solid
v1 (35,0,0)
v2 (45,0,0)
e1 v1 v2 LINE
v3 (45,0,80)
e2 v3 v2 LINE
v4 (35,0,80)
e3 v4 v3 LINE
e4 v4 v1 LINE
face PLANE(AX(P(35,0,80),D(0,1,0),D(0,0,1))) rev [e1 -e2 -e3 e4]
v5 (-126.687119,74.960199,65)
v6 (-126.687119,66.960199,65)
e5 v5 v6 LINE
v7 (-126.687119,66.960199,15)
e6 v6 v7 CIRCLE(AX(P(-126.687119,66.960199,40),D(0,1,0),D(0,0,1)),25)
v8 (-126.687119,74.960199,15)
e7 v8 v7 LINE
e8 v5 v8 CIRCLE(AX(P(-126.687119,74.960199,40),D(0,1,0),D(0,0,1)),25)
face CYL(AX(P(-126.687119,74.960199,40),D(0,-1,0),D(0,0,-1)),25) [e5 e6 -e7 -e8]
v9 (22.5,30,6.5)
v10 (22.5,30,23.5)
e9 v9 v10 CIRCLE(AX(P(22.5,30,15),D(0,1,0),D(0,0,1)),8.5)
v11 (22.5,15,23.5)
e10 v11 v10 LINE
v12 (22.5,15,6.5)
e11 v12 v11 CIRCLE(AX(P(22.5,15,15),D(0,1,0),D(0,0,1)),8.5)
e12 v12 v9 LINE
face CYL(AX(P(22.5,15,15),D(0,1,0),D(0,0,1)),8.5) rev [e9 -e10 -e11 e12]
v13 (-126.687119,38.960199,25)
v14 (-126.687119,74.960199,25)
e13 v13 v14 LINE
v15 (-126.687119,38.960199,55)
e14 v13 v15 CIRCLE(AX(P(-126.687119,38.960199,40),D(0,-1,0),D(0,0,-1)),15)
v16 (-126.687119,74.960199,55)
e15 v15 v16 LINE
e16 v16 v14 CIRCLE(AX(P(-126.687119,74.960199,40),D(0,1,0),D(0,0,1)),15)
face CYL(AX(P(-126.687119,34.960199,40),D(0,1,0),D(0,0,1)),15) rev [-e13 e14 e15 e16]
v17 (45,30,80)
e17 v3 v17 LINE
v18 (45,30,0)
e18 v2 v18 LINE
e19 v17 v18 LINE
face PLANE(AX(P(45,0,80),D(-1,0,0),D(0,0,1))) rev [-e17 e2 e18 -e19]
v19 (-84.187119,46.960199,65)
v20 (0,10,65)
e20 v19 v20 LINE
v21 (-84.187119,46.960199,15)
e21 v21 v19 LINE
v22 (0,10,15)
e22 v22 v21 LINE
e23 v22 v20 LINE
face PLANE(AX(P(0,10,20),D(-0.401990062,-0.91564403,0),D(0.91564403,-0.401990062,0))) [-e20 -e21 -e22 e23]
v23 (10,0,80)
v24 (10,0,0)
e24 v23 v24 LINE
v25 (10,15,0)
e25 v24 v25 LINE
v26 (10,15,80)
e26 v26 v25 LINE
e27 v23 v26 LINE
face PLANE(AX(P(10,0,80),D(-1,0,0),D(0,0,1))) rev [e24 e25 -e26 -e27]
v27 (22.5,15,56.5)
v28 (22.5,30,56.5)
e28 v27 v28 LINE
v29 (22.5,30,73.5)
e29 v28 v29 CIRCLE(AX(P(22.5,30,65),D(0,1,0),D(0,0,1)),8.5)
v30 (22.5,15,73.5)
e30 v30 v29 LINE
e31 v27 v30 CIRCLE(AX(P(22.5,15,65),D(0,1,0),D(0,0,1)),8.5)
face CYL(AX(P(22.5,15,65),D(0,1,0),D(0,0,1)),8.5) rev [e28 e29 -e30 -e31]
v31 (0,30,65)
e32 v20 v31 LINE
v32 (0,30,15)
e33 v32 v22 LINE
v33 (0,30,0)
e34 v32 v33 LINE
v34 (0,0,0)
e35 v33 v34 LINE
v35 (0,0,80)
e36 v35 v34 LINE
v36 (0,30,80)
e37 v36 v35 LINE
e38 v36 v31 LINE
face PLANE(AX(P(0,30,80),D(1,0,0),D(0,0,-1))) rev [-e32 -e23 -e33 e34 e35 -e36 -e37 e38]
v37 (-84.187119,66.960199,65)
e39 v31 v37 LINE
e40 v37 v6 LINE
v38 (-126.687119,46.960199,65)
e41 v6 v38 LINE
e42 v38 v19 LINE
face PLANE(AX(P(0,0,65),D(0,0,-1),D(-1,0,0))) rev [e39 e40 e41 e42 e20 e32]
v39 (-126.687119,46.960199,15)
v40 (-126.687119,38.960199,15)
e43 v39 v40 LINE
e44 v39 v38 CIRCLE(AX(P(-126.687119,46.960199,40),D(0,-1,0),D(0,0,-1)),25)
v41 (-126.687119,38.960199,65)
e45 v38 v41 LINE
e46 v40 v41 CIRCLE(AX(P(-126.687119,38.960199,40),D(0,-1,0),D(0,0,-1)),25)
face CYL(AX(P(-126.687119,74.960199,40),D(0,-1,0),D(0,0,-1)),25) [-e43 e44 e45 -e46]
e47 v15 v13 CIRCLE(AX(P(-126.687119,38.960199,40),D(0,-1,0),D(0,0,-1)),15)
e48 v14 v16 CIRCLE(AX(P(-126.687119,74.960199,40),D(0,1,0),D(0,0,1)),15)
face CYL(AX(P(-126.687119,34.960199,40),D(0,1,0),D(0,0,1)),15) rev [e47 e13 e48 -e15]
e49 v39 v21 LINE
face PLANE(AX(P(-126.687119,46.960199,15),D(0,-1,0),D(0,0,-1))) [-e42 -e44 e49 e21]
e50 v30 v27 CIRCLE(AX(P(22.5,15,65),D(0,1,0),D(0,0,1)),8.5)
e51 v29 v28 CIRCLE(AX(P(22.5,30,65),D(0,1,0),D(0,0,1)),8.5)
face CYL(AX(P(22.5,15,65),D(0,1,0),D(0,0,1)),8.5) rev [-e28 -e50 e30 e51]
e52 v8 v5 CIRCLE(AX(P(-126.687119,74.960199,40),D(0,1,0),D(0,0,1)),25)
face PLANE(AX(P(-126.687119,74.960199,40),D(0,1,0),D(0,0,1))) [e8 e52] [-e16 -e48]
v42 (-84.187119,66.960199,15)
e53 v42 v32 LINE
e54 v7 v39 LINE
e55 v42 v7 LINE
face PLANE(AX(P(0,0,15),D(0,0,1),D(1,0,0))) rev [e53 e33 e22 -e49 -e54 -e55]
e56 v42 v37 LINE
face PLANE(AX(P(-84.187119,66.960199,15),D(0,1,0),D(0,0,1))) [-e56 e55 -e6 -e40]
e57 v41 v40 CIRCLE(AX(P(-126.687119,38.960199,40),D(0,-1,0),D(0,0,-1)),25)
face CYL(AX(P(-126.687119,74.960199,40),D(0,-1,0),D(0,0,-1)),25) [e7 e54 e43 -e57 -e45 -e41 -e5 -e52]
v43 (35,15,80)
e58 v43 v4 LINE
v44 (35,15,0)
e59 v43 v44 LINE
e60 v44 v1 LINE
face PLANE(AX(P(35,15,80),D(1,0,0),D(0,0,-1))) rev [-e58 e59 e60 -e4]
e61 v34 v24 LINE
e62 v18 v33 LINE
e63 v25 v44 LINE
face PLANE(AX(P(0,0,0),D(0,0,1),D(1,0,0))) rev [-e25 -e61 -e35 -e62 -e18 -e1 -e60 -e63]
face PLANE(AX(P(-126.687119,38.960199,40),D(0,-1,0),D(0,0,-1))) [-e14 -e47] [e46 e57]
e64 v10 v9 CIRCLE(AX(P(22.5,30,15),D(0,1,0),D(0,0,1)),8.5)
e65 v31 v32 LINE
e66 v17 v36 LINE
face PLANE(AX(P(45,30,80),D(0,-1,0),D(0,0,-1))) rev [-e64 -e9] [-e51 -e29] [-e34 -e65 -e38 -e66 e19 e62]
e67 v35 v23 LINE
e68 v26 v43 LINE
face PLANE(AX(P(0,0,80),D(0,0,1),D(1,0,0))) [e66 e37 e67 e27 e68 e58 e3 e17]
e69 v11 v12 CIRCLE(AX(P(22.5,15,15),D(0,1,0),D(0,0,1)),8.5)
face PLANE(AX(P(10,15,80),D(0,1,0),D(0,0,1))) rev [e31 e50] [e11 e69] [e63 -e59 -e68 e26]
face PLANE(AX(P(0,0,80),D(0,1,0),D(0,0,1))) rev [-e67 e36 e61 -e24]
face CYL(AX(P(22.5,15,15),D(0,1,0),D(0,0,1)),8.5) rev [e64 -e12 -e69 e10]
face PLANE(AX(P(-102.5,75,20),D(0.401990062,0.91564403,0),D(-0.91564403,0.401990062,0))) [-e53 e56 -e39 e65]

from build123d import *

# Parameters (mm, degrees)
ARM_BODY_DEPTH            = 80
END_BLOCK_DEPTH           = 60
END_BLOCK_SLOT_CUT_DEPTH  = 15
END_BLOCK_PAD_5MM_DEPTH   = 5
MOUNTING_HOLES_SKETCH_R   = 8.5
MOUNTING_HOLES_2X_DEPTH   = 15
ARM_RELIEF_CUT_DEPTH      = 55
ARM_WEB_SKETCH_W          = 42.5
ARM_WEB_SKETCH_H          = 20
ARM_WEB_DEPTH             = 50
HUB_FLANGE_LOWER_SKETCH_R = 25
HUB_FLANGE_LOWER_50_DEPTH = 8
HUB_START                 = 20
HUB_BODY_DEPTH            = 20
HUB_START_2               = 8
HUB_FLANGE_UPPER_SKETCH_R = 25
HUB_FLANGE_UPPER_50_DEPTH = 8
HUB_BORE_SKETCH_R         = 15
HUB_BORE_30_DEPTH         = 40


with BuildPart() as part:
    # Arm Profile Sketch → Arm Body (new body)
    with BuildSketch(Plane.XY):
        Polygon((0, 0), (10, 0), (10, 15), (35, 15), (35, 0), (45, 0), (45, 30), (0, 30), align=None)
    extrude(amount=ARM_BODY_DEPTH)

    # End Block Sketch → End Block (add)
    with BuildSketch(Plane.XY.offset(80)):
        Polygon((-102.5, 75), (-102.5, 55), (0, 10), (0, 30), align=None)
    extrude(amount=-END_BLOCK_DEPTH)

    # End Block Slot Sketch → End Block Slot Cut (cut)
    with BuildSketch(Plane.XY.offset(80)):
        Polygon((-102.5, 75), (0, 30), (0, 10), (-102.5, 55), align=None)
    extrude(amount=-END_BLOCK_SLOT_CUT_DEPTH, mode=Mode.SUBTRACT)

    # End Block Pad Sketch → End Block Pad 5mm (add)
    with BuildSketch(Plane(origin=(0, 0, 20), x_dir=(-1, 0, 0), z_dir=(0, 0, -1))):
        Polygon((0, 30), (102.5, 75), (102.5, 55), (0, 10), align=None)
    extrude(amount=END_BLOCK_PAD_5MM_DEPTH)

    # Mounting Holes Sketch → Mounting Holes 2x (cut)
    with BuildSketch(Plane(origin=(0, 30, 0), x_dir=(1, 0, 0), z_dir=(0, 1, 0))):
        with Locations(Location((22.5, -15, 0), (0, 0, 270))):
            Circle(MOUNTING_HOLES_SKETCH_R)
        with Locations(Location((22.5, -65, 0), (0, 0, 270))):
            Circle(MOUNTING_HOLES_SKETCH_R)
    extrude(amount=-MOUNTING_HOLES_2X_DEPTH, mode=Mode.SUBTRACT)

    # Arm Relief Cut Sketch → Arm Relief Cut (cut)
    with BuildSketch(Plane.XY.offset(65)):
        Polygon((-102.5, 75), (-84.187119396, 66.960198759), (-84.187119396, 46.960198759), (-102.5, 55), align=None)
    extrude(amount=-ARM_RELIEF_CUT_DEPTH, mode=Mode.SUBTRACT)

    # Arm Web Sketch → Arm Web (add)
    with BuildSketch(Plane.XY.offset(65)):
        with Locations((-105.437119396, 56.960198759)):
            Rectangle(ARM_WEB_SKETCH_W, ARM_WEB_SKETCH_H)
    extrude(amount=-ARM_WEB_DEPTH)

    # Hub Flange Lower Sketch → Hub Flange Lower Ø50 (add)
    with BuildSketch(Plane(origin=(0, 66.960198759, 0), x_dir=(1, 0, 0), z_dir=(0, 1, 0))):
        with Locations(Location((-126.687119396, -40, 0), (0, 0, 270))):
            Circle(HUB_FLANGE_LOWER_SKETCH_R)
    extrude(amount=HUB_FLANGE_LOWER_50_DEPTH)

    # Hub Body Sketch → Hub Body (add)
    with BuildSketch(Plane.XZ.offset(-66.960198759).offset(HUB_START)):
        with BuildLine():
            Line((-126.687119396, 65), (-126.687119396, 15))
            ThreePointArc((-126.687119396, 15), (-151.687119396, 40), (-126.687119396, 65))
        make_face()
    extrude(amount=-HUB_BODY_DEPTH)

    # Hub Flange Upper Sketch → Hub Flange Upper Ø50 (add)
    with BuildSketch(Plane.XZ.offset(-46.960198759).offset(HUB_START_2)):
        with Locations(Location((-126.687119396, 40, 0), (0, 0, 270))):
            Circle(HUB_FLANGE_UPPER_SKETCH_R)
    extrude(amount=-HUB_FLANGE_UPPER_50_DEPTH)

    # Hub Bore Sketch → Hub Bore Ø30 (cut)
    with BuildSketch(Plane(origin=(0, 74.960198759, 0), x_dir=(1, 0, 0), z_dir=(0, 1, 0))):
        with Locations(Location((-126.687119396, -40, 0), (0, 0, 270))):
            Circle(HUB_BORE_SKETCH_R)
    extrude(amount=-HUB_BORE_30_DEPTH, mode=Mode.SUBTRACT)


solid = part.part
